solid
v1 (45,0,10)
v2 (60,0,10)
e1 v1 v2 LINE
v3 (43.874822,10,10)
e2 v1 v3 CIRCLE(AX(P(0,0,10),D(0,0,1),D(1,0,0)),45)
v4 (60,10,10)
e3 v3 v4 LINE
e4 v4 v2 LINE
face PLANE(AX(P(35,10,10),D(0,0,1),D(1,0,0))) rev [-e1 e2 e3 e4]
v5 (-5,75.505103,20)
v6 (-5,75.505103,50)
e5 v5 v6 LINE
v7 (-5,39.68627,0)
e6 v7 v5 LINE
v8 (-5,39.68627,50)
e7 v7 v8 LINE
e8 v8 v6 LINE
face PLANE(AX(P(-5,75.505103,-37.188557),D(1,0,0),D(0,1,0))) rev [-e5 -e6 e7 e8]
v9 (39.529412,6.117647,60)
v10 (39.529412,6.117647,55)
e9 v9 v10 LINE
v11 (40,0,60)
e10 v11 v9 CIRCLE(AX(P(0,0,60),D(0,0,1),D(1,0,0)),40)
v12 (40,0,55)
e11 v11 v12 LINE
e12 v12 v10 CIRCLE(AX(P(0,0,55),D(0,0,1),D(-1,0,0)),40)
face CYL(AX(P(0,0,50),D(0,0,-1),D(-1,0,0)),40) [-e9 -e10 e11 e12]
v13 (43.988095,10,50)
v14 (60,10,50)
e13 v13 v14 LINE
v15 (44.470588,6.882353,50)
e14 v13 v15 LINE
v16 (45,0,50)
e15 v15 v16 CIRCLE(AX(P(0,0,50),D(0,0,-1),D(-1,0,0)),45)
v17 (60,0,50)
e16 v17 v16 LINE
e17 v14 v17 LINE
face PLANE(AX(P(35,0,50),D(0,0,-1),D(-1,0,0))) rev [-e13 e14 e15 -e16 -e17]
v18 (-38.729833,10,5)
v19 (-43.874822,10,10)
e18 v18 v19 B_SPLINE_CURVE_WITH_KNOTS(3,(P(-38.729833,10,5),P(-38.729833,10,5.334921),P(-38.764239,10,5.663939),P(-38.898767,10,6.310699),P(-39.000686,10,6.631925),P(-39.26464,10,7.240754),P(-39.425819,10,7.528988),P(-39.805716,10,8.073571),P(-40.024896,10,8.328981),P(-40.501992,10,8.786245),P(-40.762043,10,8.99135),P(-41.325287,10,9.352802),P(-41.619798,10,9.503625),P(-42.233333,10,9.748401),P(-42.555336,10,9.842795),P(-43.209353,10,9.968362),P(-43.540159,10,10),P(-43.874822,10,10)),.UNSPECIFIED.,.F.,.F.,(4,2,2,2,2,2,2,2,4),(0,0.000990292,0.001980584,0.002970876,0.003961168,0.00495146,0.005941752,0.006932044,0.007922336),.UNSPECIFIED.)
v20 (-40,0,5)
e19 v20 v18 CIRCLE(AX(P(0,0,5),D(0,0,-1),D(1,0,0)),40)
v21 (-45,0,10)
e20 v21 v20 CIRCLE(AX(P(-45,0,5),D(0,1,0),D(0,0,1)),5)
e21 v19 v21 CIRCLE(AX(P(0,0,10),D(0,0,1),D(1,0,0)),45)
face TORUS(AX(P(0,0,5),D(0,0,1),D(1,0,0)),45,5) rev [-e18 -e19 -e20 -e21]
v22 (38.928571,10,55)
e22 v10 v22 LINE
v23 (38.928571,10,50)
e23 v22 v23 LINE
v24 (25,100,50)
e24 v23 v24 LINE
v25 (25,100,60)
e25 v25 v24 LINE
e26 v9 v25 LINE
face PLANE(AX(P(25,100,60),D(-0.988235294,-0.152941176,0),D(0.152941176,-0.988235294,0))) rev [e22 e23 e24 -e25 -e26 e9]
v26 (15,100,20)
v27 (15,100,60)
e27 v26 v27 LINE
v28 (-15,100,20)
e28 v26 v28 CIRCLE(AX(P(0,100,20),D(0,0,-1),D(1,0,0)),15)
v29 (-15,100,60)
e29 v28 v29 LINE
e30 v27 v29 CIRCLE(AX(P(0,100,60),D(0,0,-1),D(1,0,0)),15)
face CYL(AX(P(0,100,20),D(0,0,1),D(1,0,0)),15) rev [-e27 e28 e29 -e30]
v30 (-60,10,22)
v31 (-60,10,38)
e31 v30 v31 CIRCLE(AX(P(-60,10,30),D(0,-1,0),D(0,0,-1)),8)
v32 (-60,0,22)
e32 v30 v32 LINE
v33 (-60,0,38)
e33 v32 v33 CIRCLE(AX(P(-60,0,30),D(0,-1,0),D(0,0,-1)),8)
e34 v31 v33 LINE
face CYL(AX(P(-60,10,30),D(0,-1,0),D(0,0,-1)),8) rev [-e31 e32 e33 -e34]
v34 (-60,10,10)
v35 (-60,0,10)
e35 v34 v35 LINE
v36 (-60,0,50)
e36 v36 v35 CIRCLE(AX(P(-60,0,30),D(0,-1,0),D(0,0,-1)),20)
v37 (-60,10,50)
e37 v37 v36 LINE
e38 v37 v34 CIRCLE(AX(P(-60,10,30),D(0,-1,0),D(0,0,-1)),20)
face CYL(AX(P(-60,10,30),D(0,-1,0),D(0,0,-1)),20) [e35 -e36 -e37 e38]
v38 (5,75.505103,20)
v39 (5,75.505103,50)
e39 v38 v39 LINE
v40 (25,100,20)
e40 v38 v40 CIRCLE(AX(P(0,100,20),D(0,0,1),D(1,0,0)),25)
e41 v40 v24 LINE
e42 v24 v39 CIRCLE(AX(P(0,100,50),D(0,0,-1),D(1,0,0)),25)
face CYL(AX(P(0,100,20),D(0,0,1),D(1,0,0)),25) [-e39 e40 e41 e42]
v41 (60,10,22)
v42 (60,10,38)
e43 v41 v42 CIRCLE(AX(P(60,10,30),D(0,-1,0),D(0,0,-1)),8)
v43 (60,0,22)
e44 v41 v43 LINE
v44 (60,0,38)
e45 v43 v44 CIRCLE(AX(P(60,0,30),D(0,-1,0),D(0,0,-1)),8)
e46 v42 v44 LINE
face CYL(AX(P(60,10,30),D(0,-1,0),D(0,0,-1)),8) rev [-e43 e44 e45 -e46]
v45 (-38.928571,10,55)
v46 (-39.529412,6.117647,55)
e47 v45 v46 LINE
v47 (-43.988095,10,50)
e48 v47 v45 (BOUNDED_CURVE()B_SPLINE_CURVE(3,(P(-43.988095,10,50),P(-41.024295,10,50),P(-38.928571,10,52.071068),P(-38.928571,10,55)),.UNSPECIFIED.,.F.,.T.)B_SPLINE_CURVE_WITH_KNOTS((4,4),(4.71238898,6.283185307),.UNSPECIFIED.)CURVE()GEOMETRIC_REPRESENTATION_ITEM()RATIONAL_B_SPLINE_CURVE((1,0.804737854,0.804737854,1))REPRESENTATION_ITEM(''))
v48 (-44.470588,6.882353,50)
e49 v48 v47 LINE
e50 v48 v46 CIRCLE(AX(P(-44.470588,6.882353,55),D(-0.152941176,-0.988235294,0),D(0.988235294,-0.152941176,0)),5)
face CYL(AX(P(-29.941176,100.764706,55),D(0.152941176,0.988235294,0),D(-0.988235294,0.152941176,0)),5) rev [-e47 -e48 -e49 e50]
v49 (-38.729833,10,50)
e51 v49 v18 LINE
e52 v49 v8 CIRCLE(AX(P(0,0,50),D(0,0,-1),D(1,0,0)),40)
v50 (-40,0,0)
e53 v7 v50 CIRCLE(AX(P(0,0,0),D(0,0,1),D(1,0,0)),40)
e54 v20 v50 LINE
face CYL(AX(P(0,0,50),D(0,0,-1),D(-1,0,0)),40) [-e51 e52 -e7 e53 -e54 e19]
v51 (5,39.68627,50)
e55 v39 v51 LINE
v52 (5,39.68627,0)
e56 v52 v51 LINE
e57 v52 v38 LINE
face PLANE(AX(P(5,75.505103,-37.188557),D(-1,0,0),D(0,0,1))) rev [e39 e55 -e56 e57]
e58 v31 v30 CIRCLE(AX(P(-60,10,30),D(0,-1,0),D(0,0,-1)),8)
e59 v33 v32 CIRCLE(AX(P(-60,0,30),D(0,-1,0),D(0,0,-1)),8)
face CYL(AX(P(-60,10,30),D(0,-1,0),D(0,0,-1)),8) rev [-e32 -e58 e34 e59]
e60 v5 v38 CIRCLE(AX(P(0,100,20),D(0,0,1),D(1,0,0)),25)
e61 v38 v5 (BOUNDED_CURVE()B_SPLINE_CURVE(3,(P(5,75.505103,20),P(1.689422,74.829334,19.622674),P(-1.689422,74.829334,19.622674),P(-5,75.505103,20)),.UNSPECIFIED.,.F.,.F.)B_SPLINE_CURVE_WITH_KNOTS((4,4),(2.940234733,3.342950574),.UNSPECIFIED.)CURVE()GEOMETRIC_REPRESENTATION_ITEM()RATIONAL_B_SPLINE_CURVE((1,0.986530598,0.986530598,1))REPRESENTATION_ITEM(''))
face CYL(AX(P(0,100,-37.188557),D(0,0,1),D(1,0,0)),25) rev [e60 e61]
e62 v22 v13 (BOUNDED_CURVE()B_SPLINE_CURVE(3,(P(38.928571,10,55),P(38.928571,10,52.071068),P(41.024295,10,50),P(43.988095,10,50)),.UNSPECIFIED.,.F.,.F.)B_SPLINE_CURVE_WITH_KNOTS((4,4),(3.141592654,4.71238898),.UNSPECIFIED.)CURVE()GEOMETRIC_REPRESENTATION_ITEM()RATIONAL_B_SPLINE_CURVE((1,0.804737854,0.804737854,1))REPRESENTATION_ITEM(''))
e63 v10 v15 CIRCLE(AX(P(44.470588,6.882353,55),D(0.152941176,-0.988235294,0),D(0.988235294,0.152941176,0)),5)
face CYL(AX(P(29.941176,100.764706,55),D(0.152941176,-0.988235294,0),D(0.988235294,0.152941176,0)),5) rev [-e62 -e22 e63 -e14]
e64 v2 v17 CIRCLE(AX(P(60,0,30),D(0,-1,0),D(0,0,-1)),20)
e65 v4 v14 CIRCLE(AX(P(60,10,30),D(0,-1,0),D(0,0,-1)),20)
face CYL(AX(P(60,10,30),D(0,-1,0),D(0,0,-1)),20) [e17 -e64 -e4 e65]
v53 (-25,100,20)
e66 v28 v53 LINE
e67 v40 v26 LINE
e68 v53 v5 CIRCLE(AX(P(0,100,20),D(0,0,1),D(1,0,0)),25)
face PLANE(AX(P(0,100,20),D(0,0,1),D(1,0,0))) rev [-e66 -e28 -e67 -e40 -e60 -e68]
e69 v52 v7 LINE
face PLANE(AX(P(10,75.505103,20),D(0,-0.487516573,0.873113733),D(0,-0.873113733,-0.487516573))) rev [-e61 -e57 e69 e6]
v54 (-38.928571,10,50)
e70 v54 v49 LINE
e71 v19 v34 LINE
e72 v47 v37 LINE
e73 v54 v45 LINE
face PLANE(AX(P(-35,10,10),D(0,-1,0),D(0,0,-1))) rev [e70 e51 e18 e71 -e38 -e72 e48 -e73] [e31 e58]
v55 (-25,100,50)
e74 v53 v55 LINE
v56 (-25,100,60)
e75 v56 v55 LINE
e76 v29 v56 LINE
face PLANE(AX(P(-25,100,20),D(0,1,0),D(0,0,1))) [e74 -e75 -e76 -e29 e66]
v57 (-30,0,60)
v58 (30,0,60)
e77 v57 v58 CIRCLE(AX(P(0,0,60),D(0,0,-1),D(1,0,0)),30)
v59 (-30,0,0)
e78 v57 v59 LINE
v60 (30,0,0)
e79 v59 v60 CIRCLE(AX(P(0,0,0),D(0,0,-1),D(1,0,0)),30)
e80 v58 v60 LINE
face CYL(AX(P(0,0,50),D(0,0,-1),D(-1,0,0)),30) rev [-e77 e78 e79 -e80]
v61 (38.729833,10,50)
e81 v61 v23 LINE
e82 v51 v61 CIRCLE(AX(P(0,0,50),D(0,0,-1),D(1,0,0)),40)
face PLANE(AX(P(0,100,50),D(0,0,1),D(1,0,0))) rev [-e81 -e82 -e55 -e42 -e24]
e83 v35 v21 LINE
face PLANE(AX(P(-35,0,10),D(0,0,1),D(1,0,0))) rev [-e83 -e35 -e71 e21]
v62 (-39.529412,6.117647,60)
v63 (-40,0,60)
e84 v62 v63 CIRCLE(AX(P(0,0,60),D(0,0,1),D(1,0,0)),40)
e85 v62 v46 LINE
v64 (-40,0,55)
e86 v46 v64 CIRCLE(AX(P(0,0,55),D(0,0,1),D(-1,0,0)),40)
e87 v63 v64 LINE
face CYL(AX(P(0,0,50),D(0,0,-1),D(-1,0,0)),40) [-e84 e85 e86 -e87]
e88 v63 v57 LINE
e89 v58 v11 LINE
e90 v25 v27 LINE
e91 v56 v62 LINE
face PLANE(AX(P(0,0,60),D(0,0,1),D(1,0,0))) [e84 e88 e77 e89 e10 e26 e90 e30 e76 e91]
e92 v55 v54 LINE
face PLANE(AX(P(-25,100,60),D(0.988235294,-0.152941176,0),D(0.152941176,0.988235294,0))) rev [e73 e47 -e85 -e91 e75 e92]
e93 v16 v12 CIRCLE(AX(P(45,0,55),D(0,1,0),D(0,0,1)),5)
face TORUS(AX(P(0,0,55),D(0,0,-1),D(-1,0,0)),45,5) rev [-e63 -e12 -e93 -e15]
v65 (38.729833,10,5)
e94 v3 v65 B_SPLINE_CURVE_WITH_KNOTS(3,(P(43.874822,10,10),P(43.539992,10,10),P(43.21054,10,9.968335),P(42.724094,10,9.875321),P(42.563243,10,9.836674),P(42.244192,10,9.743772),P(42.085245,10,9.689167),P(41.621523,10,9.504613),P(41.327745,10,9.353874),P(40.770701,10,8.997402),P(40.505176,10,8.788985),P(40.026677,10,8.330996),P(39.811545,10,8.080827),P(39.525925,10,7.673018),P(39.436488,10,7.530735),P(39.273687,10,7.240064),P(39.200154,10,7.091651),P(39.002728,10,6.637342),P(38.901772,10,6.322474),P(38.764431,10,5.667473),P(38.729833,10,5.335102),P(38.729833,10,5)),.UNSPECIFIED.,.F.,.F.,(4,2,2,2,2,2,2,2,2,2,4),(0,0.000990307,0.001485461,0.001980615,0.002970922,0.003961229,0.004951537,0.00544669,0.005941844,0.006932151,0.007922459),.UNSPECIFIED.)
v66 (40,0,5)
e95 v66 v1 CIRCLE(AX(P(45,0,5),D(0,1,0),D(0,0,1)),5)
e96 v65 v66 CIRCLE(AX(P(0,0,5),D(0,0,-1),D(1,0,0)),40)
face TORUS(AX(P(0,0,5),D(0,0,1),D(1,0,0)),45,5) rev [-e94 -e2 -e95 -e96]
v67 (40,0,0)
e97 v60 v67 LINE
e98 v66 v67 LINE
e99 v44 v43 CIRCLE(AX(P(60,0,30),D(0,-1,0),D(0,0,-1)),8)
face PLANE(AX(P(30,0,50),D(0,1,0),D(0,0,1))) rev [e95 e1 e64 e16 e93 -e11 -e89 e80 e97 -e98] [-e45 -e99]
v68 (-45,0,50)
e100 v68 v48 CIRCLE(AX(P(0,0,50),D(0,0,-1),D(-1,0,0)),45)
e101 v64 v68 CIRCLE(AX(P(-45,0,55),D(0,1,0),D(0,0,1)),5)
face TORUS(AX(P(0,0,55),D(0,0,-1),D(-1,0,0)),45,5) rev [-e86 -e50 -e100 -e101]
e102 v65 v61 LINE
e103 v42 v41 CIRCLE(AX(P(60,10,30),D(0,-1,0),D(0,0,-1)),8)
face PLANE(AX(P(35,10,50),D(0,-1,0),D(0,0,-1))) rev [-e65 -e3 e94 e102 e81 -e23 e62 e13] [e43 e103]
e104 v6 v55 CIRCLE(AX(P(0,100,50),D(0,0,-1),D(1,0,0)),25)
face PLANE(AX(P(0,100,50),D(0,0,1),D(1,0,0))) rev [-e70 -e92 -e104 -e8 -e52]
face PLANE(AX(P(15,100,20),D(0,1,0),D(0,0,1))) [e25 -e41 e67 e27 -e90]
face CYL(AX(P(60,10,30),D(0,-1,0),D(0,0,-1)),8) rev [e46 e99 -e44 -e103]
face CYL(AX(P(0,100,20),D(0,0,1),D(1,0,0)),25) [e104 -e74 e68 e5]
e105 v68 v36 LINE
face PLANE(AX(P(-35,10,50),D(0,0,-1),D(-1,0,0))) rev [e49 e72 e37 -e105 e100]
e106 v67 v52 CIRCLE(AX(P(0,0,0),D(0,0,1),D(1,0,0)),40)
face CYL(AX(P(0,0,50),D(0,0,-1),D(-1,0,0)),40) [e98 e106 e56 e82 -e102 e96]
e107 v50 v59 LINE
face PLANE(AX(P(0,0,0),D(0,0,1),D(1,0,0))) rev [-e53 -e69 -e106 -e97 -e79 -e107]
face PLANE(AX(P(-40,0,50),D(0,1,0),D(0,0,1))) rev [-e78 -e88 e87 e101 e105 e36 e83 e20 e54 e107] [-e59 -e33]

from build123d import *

# Parameters (mm, degrees)
BASE_BLOCK_DEPTH        = 50
UPRIGHT_BODY_DEPTH      = 30
SADDLE_FLANGE_DEPTH     = 10
SIDE_BOSS_1_DEPTH       = 10
SIDE_BOSS_2_DEPTH       = 10
MOUNTING_LUG_1_SKETCH_R = 8
MOUNTING_LUG_1_DEPTH    = 10
LUG_1_BOSS_SKETCH_W     = 40
LUG_1_BOSS_SKETCH_H     = 10
LUG_1_BOSS_DEPTH        = 5
LUG_1_FILLET_R5_R       = 5
MOUNTING_LUG_2_SKETCH_R = 8
MOUNTING_LUG_2_DEPTH    = 10
LUG_2_BOSS_SKETCH_W     = 40
LUG_2_BOSS_SKETCH_H     = 10
LUG_2_BOSS_DEPTH        = 5
LUG_2_FILLET_R5_R       = 5
SIDE_RIB_DEPTH          = 50
RIB_RELIEF_CUT_DEPTH    = 15


with BuildPart() as part:
    # Base Profile Sketch → Base Block (new body)
    with BuildSketch(Plane.XY):
        with BuildLine():
            Line((-40, 0), (-30, 0))
            ThreePointArc((-30, 0), (0, 30), (30, 0))
            Line((30, 0), (40, 0))
            ThreePointArc((40, 0), (0, 40), (-40, 0))
        make_face()
    extrude(amount=BASE_BLOCK_DEPTH)



with BuildPart() as body_2:
    # Upright Profile Sketch → Upright Body (new body)
    with BuildSketch(Plane.XY.offset(50)):
        with BuildLine():
            Line((-25, 100), (-15, 100))
            ThreePointArc((-15, 100), (0, 85), (15, 100))
            Line((15, 100), (25, 100))
            ThreePointArc((25, 100), (0, 75), (-25, 100))
        make_face()
    extrude(amount=-UPRIGHT_BODY_DEPTH)



with BuildPart() as body_3:
    # Saddle Flange Sketch → Saddle Flange (new body)
    with BuildSketch(Plane.XY.offset(50)):
        with BuildLine():
            Line((-25, 100), (-39.529411765, 6.117647059))
            ThreePointArc((-39.529411765, 6.117647059), (0, 40), (39.529411765, 6.117647059))
            Line((39.529411765, 6.117647059), (25, 100))
            ThreePointArc((25, 100), (0, 75), (-25, 100))
        make_face()
    extrude(amount=SADDLE_FLANGE_DEPTH)


with BuildPart() as body_2_1:
    add(body_2.part)

    add(body_3.part)  # Side Boss 1 merges body 3
    # Side Boss 1 Sketch → Side Boss 1 (add)
    with BuildSketch(Plane.XY.offset(50)):
        with BuildLine():
            Line((-15, 100), (-25, 100))
            ThreePointArc((-25, 100), (0, 75), (25, 100))
            Line((25, 100), (15, 100))
            ThreePointArc((15, 100), (0, 85), (-15, 100))
        make_face()
    extrude(amount=SIDE_BOSS_1_DEPTH)


with BuildPart() as part_1:
    add(part.part)

    add(body_2_1.part)  # Side Boss 2 merges body 2
    # Side Boss 2 Sketch → Side Boss 2 (add)
    with BuildSketch(Plane.XY.offset(50)):
        with BuildLine():
            Line((30, 0), (40, 0))
            ThreePointArc((40, 0), (0, 40), (-40, 0))
            Line((-40, 0), (-30, 0))
            ThreePointArc((-30, 0), (0, 30), (30, 0))
        make_face()
    extrude(amount=SIDE_BOSS_2_DEPTH)



with BuildPart() as body_2_2:
    # Mounting Lug 1 Sketch → Mounting Lug 1 (new body)
    with BuildSketch(Plane.XZ):
        with BuildLine():
            Line((-60, 50), (-40, 50))
            Line((-40, 50), (-40, 10))
            Line((-40, 10), (-60, 10))
            ThreePointArc((-60, 10), (-80, 30), (-60, 50))
        make_face()
        with Locations(Location((-60, 30, 0), (0, 0, 270))):
            Circle(MOUNTING_LUG_1_SKETCH_R, mode=Mode.SUBTRACT)
    extrude(amount=-MOUNTING_LUG_1_DEPTH)


with BuildPart() as part_2:
    add(part_1.part)

    add(body_2_2.part)  # Lug 1 Boss merges body 2 2
    # Lug 1 Boss Sketch → Lug 1 Boss (add)
    with BuildSketch(Plane(origin=(-40, 0, 0), x_dir=(0, 0, -1), z_dir=(1, 0, 0))):
        with Locations((-30, 5)):
            Rectangle(LUG_1_BOSS_SKETCH_W, LUG_1_BOSS_SKETCH_H)
    extrude(amount=LUG_1_BOSS_DEPTH)

    # Lug 1 Fillet R5
    lug_1_fillet_r5_edges = [part_2.edges().sort_by_distance(p)[0] for p in [
        (-39.228991597, 8.058823529, 50),
        (-39.681187851, 5.040171699, 10),
        (-39.88217942, 3.067859955, 50),
    ]]
    fillet(lug_1_fillet_r5_edges, radius=LUG_1_FILLET_R5_R)



with BuildPart() as body_2_3:
    # Mounting Lug 2 Sketch → Mounting Lug 2 (new body)
    with BuildSketch(Plane.XZ):
        with BuildLine():
            Line((60, 50), (40, 50))
            Line((40, 50), (40, 10))
            Line((40, 10), (60, 10))
            ThreePointArc((60, 10), (80, 30), (60, 50))
        make_face()
        with Locations(Location((60, 30, 0), (0, 0, 270))):
            Circle(MOUNTING_LUG_2_SKETCH_R, mode=Mode.SUBTRACT)
    extrude(amount=-MOUNTING_LUG_2_DEPTH)


with BuildPart() as part_3:
    add(part_2.part)

    add(body_2_3.part)  # Lug 2 Boss merges body 2 3
    # Lug 2 Boss Sketch → Lug 2 Boss (add)
    with BuildSketch(Plane.ZY.offset(-40)):
        with Locations((30, 5)):
            Rectangle(LUG_2_BOSS_SKETCH_W, LUG_2_BOSS_SKETCH_H)
    extrude(amount=LUG_2_BOSS_DEPTH)

    # Lug 2 Fillet R5
    lug_2_fillet_r5_edges = [part_3.edges().sort_by_distance(p)[0] for p in [
        (39.681187851, 5.040171699, 10),
        (39.88217942, 3.067859955, 50),
        (39.228991597, 8.058823529, 50),
    ]]
    fillet(lug_2_fillet_r5_edges, radius=LUG_2_FILLET_R5_R)

    # Side Rib Sketch → Side Rib (add)
    with BuildSketch(Plane(origin=(0, 0, 50), x_dir=(-1, 0, 0), z_dir=(0, 0, -1))):
        with BuildLine():
            Line((-5, 75.505102572), (-5, 39.686269666))
            ThreePointArc((-5, 39.686269666), (0, 40), (5, 39.686269666))
            Line((5, 39.686269666), (5, 75.505102572))
            ThreePointArc((5, 75.505102572), (0, 75), (-5, 75.505102572))
        make_face()
    extrude(amount=SIDE_RIB_DEPTH)

    # Rib Relief Cut Sketch → Rib Relief Cut (cut)
    with BuildSketch(Plane.ZY.offset(5)):
        Polygon((20, 75.505102572), (0, 39.686269666), (0, 75.505102572), align=None)
    extrude(amount=-RIB_RELIEF_CUT_DEPTH, mode=Mode.SUBTRACT)


solid = part_3.part
